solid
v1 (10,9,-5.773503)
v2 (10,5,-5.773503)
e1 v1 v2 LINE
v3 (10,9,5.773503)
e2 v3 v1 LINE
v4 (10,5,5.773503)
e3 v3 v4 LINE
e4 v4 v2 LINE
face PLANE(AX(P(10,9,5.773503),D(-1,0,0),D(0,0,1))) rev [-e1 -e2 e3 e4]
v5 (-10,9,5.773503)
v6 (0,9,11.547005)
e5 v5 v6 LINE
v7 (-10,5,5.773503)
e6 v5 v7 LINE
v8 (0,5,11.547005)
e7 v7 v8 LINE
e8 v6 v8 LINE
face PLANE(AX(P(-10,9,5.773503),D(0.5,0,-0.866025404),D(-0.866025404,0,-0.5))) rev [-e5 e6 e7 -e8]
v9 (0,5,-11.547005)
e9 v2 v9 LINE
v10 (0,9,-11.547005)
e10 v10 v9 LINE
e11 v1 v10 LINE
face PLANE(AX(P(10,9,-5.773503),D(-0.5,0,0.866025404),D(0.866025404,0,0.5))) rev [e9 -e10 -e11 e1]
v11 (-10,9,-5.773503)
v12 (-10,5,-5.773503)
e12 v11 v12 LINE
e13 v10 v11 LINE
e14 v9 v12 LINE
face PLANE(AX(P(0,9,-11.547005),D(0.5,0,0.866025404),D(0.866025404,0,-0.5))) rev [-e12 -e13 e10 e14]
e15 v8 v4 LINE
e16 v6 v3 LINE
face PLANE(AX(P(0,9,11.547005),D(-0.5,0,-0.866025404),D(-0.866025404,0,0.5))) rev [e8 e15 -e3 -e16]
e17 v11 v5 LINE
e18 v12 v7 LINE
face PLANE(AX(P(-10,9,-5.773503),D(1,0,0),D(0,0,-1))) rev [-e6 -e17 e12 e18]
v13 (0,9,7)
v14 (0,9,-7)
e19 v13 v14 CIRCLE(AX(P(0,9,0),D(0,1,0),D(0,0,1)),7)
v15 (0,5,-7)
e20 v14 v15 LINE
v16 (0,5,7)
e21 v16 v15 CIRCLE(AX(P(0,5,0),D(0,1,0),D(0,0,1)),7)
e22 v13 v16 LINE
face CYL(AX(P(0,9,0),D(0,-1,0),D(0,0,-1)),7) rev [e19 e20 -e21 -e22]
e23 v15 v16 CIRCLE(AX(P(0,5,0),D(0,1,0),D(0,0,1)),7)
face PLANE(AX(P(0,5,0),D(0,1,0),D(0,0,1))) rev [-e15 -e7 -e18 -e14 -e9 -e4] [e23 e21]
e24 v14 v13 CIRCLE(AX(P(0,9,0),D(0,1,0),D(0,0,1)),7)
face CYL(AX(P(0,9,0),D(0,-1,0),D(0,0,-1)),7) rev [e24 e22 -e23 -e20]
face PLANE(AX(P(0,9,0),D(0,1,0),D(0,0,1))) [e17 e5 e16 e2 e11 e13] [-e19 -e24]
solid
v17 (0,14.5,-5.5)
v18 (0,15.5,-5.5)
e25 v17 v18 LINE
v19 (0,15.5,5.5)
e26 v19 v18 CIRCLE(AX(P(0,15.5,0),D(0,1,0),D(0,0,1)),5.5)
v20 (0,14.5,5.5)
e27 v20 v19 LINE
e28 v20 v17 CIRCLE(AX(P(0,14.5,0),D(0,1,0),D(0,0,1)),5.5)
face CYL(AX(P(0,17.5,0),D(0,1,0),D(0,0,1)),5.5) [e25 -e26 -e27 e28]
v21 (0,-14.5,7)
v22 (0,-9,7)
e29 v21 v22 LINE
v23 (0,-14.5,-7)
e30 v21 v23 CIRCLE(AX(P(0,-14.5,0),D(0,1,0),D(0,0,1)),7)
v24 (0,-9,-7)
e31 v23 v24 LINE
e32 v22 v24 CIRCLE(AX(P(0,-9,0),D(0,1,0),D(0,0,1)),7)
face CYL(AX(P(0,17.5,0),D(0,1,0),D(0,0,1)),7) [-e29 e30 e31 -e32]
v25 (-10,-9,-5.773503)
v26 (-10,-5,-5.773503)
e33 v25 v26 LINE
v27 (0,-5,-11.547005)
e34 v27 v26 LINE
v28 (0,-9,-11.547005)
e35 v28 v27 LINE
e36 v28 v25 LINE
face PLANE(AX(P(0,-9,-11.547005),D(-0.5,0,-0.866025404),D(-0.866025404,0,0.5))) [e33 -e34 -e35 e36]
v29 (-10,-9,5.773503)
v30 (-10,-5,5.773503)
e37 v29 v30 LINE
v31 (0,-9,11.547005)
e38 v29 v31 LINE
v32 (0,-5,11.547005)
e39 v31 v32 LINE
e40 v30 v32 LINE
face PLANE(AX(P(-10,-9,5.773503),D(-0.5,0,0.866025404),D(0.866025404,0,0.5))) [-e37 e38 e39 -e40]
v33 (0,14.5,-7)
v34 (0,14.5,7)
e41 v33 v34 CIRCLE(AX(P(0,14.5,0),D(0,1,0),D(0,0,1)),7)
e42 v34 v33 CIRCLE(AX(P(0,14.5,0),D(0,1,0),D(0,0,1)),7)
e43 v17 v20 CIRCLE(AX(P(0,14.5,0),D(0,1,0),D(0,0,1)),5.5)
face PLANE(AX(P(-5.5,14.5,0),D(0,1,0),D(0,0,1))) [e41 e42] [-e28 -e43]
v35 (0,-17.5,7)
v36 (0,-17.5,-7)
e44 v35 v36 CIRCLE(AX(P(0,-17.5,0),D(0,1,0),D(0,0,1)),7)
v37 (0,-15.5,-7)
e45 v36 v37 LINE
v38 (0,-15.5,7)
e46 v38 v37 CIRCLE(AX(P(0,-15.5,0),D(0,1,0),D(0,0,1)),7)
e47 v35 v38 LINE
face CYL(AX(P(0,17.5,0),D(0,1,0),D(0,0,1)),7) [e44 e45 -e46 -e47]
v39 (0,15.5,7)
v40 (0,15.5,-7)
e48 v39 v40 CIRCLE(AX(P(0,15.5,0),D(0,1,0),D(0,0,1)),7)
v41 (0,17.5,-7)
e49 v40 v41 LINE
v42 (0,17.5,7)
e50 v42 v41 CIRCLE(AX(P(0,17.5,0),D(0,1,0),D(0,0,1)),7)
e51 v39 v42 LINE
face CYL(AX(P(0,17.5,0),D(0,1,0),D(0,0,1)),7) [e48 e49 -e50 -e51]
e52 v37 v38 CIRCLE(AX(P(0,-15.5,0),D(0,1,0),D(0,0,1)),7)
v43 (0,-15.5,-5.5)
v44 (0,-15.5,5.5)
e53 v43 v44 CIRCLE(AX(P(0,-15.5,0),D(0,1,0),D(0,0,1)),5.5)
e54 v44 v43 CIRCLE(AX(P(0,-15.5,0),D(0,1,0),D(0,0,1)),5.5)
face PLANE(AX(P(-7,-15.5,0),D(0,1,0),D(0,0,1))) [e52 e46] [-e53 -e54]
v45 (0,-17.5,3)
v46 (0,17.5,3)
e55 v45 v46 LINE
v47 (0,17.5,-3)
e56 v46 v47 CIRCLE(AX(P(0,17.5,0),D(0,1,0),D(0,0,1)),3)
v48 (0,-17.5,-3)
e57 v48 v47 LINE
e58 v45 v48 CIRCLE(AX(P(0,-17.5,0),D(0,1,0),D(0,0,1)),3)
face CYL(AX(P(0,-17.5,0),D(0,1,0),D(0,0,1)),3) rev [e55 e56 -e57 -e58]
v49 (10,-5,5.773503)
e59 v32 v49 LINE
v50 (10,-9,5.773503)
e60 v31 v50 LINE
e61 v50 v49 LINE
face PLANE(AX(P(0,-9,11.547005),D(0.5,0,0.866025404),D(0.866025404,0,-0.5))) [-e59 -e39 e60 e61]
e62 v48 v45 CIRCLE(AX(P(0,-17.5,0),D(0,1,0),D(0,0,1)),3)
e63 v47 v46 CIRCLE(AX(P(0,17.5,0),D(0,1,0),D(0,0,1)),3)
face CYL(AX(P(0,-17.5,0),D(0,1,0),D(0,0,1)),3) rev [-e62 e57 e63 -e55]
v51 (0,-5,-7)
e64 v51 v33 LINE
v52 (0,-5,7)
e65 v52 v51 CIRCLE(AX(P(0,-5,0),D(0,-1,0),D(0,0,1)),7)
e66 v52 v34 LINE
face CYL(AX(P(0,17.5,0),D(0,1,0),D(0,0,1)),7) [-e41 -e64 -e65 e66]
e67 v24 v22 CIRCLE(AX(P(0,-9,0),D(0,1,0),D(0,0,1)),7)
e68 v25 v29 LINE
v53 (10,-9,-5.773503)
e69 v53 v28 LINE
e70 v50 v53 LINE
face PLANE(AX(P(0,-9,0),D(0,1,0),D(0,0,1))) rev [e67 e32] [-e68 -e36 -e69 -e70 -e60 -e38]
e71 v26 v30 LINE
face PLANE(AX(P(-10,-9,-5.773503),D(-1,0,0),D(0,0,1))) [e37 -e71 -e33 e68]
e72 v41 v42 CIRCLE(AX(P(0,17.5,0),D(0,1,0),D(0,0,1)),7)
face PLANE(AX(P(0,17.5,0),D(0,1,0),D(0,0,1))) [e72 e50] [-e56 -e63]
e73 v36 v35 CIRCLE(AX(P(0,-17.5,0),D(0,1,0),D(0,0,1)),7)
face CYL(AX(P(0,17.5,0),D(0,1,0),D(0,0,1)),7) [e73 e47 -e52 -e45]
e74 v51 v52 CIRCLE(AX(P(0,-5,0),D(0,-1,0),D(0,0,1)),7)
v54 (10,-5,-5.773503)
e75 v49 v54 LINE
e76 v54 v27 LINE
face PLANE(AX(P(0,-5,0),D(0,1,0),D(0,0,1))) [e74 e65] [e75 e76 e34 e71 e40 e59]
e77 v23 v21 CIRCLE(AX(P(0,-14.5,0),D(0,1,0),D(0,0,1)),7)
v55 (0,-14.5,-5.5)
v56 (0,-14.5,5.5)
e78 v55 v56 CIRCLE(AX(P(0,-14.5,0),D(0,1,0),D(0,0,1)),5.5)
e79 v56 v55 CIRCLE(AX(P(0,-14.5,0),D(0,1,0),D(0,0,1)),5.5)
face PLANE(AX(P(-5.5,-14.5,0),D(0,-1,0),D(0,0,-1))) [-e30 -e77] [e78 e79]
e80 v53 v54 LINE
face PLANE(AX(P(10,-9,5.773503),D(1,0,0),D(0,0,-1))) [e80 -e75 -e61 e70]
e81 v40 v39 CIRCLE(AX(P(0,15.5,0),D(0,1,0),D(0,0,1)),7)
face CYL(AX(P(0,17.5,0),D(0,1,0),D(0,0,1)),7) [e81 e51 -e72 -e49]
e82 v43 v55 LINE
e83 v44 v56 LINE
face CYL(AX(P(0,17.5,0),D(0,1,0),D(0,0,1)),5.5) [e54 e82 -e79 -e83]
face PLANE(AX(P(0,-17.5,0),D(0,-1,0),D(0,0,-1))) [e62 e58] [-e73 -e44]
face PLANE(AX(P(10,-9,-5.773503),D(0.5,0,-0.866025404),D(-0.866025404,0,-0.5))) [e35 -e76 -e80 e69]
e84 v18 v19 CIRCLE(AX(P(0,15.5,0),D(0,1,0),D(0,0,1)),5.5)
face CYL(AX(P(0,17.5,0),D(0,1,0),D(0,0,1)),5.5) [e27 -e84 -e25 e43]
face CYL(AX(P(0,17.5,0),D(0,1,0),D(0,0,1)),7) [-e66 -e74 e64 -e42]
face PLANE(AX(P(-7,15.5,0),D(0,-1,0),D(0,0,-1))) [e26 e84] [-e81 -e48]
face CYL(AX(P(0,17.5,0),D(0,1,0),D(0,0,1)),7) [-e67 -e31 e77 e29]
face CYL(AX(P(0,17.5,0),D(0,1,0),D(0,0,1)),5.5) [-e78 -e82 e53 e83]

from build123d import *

# Parameters (mm, degrees)
SKETCH2_R           = 3
CUT_EXTRUDE1_DEPTH  = 37.373066959
SKETCH3_R           = 7
BOSS_EXTRUDE1_DEPTH = 4
BOSS_EXTRUDE2_START = -4
SKETCH4_R           = 7
BOSS_EXTRUDE2_DEPTH = 4


with BuildPart() as part:
    # Sketch1 → Revolve1 (revolve)
    with BuildSketch(Plane.XY, mode=Mode.PRIVATE) as revolve1_sk:
        Polygon((0, 17.5), (-7, 17.5), (-7, 15.5), (-5.5, 15.5), (-5.5, 14.5), (-7, 14.5), (-7, -14.5), (-5.5, -14.5), (-5.5, -15.5), (-7, -15.5), (-7, -17.5), (0, -17.5), align=None)
    revolve(revolve1_sk.sketch.rotate(Axis((0, 17.5, 0), (0, -1, 0)), 270), axis=Axis((0, 17.5, 0), (0, -1, 0)))

    # Sketch2 → Cut-Extrude1 (cut, through all)
    with BuildSketch(Plane(origin=(0, 17.5, 0), x_dir=(1, 0, 0), z_dir=(0, 1, 0))):
        with Locations(Location((0, 0, 0), (0, 0, 270))):
            Circle(SKETCH2_R)
    extrude(amount=-CUT_EXTRUDE1_DEPTH, mode=Mode.SUBTRACT)

    # Sketch4 → Boss-Extrude2 (add)
    with BuildSketch(Plane(origin=(0, -5, 0), x_dir=(1, 0, 0), z_dir=(0, 1, 0)).offset(BOSS_EXTRUDE2_START)):
        Polygon((0, 11.547005384), (-10, 5.773502692), (-10, -5.773502692), (0, -11.547005384), (10, -5.773502692), (10, 5.773502692), align=None)
        with Locations(Location((0, 0, 0), (0, 0, 270))):
            Circle(SKETCH4_R, mode=Mode.SUBTRACT)
    extrude(amount=BOSS_EXTRUDE2_DEPTH)


with BuildPart() as body_2:
    # Sketch3 → Boss-Extrude1 (new body)
    with BuildSketch(Plane(origin=(0, 5, 0), x_dir=(1, 0, 0), z_dir=(0, 1, 0))):
        Polygon((0, 11.547005384), (-10, 5.773502692), (-10, -5.773502692), (0, -11.547005384), (10, -5.773502692), (10, 5.773502692), align=None)
        with Locations(Location((0, 0, 0), (0, 0, 270))):
            Circle(SKETCH3_R, mode=Mode.SUBTRACT)
    extrude(amount=BOSS_EXTRUDE1_DEPTH)


solid = Compound([part.part, body_2.part])
